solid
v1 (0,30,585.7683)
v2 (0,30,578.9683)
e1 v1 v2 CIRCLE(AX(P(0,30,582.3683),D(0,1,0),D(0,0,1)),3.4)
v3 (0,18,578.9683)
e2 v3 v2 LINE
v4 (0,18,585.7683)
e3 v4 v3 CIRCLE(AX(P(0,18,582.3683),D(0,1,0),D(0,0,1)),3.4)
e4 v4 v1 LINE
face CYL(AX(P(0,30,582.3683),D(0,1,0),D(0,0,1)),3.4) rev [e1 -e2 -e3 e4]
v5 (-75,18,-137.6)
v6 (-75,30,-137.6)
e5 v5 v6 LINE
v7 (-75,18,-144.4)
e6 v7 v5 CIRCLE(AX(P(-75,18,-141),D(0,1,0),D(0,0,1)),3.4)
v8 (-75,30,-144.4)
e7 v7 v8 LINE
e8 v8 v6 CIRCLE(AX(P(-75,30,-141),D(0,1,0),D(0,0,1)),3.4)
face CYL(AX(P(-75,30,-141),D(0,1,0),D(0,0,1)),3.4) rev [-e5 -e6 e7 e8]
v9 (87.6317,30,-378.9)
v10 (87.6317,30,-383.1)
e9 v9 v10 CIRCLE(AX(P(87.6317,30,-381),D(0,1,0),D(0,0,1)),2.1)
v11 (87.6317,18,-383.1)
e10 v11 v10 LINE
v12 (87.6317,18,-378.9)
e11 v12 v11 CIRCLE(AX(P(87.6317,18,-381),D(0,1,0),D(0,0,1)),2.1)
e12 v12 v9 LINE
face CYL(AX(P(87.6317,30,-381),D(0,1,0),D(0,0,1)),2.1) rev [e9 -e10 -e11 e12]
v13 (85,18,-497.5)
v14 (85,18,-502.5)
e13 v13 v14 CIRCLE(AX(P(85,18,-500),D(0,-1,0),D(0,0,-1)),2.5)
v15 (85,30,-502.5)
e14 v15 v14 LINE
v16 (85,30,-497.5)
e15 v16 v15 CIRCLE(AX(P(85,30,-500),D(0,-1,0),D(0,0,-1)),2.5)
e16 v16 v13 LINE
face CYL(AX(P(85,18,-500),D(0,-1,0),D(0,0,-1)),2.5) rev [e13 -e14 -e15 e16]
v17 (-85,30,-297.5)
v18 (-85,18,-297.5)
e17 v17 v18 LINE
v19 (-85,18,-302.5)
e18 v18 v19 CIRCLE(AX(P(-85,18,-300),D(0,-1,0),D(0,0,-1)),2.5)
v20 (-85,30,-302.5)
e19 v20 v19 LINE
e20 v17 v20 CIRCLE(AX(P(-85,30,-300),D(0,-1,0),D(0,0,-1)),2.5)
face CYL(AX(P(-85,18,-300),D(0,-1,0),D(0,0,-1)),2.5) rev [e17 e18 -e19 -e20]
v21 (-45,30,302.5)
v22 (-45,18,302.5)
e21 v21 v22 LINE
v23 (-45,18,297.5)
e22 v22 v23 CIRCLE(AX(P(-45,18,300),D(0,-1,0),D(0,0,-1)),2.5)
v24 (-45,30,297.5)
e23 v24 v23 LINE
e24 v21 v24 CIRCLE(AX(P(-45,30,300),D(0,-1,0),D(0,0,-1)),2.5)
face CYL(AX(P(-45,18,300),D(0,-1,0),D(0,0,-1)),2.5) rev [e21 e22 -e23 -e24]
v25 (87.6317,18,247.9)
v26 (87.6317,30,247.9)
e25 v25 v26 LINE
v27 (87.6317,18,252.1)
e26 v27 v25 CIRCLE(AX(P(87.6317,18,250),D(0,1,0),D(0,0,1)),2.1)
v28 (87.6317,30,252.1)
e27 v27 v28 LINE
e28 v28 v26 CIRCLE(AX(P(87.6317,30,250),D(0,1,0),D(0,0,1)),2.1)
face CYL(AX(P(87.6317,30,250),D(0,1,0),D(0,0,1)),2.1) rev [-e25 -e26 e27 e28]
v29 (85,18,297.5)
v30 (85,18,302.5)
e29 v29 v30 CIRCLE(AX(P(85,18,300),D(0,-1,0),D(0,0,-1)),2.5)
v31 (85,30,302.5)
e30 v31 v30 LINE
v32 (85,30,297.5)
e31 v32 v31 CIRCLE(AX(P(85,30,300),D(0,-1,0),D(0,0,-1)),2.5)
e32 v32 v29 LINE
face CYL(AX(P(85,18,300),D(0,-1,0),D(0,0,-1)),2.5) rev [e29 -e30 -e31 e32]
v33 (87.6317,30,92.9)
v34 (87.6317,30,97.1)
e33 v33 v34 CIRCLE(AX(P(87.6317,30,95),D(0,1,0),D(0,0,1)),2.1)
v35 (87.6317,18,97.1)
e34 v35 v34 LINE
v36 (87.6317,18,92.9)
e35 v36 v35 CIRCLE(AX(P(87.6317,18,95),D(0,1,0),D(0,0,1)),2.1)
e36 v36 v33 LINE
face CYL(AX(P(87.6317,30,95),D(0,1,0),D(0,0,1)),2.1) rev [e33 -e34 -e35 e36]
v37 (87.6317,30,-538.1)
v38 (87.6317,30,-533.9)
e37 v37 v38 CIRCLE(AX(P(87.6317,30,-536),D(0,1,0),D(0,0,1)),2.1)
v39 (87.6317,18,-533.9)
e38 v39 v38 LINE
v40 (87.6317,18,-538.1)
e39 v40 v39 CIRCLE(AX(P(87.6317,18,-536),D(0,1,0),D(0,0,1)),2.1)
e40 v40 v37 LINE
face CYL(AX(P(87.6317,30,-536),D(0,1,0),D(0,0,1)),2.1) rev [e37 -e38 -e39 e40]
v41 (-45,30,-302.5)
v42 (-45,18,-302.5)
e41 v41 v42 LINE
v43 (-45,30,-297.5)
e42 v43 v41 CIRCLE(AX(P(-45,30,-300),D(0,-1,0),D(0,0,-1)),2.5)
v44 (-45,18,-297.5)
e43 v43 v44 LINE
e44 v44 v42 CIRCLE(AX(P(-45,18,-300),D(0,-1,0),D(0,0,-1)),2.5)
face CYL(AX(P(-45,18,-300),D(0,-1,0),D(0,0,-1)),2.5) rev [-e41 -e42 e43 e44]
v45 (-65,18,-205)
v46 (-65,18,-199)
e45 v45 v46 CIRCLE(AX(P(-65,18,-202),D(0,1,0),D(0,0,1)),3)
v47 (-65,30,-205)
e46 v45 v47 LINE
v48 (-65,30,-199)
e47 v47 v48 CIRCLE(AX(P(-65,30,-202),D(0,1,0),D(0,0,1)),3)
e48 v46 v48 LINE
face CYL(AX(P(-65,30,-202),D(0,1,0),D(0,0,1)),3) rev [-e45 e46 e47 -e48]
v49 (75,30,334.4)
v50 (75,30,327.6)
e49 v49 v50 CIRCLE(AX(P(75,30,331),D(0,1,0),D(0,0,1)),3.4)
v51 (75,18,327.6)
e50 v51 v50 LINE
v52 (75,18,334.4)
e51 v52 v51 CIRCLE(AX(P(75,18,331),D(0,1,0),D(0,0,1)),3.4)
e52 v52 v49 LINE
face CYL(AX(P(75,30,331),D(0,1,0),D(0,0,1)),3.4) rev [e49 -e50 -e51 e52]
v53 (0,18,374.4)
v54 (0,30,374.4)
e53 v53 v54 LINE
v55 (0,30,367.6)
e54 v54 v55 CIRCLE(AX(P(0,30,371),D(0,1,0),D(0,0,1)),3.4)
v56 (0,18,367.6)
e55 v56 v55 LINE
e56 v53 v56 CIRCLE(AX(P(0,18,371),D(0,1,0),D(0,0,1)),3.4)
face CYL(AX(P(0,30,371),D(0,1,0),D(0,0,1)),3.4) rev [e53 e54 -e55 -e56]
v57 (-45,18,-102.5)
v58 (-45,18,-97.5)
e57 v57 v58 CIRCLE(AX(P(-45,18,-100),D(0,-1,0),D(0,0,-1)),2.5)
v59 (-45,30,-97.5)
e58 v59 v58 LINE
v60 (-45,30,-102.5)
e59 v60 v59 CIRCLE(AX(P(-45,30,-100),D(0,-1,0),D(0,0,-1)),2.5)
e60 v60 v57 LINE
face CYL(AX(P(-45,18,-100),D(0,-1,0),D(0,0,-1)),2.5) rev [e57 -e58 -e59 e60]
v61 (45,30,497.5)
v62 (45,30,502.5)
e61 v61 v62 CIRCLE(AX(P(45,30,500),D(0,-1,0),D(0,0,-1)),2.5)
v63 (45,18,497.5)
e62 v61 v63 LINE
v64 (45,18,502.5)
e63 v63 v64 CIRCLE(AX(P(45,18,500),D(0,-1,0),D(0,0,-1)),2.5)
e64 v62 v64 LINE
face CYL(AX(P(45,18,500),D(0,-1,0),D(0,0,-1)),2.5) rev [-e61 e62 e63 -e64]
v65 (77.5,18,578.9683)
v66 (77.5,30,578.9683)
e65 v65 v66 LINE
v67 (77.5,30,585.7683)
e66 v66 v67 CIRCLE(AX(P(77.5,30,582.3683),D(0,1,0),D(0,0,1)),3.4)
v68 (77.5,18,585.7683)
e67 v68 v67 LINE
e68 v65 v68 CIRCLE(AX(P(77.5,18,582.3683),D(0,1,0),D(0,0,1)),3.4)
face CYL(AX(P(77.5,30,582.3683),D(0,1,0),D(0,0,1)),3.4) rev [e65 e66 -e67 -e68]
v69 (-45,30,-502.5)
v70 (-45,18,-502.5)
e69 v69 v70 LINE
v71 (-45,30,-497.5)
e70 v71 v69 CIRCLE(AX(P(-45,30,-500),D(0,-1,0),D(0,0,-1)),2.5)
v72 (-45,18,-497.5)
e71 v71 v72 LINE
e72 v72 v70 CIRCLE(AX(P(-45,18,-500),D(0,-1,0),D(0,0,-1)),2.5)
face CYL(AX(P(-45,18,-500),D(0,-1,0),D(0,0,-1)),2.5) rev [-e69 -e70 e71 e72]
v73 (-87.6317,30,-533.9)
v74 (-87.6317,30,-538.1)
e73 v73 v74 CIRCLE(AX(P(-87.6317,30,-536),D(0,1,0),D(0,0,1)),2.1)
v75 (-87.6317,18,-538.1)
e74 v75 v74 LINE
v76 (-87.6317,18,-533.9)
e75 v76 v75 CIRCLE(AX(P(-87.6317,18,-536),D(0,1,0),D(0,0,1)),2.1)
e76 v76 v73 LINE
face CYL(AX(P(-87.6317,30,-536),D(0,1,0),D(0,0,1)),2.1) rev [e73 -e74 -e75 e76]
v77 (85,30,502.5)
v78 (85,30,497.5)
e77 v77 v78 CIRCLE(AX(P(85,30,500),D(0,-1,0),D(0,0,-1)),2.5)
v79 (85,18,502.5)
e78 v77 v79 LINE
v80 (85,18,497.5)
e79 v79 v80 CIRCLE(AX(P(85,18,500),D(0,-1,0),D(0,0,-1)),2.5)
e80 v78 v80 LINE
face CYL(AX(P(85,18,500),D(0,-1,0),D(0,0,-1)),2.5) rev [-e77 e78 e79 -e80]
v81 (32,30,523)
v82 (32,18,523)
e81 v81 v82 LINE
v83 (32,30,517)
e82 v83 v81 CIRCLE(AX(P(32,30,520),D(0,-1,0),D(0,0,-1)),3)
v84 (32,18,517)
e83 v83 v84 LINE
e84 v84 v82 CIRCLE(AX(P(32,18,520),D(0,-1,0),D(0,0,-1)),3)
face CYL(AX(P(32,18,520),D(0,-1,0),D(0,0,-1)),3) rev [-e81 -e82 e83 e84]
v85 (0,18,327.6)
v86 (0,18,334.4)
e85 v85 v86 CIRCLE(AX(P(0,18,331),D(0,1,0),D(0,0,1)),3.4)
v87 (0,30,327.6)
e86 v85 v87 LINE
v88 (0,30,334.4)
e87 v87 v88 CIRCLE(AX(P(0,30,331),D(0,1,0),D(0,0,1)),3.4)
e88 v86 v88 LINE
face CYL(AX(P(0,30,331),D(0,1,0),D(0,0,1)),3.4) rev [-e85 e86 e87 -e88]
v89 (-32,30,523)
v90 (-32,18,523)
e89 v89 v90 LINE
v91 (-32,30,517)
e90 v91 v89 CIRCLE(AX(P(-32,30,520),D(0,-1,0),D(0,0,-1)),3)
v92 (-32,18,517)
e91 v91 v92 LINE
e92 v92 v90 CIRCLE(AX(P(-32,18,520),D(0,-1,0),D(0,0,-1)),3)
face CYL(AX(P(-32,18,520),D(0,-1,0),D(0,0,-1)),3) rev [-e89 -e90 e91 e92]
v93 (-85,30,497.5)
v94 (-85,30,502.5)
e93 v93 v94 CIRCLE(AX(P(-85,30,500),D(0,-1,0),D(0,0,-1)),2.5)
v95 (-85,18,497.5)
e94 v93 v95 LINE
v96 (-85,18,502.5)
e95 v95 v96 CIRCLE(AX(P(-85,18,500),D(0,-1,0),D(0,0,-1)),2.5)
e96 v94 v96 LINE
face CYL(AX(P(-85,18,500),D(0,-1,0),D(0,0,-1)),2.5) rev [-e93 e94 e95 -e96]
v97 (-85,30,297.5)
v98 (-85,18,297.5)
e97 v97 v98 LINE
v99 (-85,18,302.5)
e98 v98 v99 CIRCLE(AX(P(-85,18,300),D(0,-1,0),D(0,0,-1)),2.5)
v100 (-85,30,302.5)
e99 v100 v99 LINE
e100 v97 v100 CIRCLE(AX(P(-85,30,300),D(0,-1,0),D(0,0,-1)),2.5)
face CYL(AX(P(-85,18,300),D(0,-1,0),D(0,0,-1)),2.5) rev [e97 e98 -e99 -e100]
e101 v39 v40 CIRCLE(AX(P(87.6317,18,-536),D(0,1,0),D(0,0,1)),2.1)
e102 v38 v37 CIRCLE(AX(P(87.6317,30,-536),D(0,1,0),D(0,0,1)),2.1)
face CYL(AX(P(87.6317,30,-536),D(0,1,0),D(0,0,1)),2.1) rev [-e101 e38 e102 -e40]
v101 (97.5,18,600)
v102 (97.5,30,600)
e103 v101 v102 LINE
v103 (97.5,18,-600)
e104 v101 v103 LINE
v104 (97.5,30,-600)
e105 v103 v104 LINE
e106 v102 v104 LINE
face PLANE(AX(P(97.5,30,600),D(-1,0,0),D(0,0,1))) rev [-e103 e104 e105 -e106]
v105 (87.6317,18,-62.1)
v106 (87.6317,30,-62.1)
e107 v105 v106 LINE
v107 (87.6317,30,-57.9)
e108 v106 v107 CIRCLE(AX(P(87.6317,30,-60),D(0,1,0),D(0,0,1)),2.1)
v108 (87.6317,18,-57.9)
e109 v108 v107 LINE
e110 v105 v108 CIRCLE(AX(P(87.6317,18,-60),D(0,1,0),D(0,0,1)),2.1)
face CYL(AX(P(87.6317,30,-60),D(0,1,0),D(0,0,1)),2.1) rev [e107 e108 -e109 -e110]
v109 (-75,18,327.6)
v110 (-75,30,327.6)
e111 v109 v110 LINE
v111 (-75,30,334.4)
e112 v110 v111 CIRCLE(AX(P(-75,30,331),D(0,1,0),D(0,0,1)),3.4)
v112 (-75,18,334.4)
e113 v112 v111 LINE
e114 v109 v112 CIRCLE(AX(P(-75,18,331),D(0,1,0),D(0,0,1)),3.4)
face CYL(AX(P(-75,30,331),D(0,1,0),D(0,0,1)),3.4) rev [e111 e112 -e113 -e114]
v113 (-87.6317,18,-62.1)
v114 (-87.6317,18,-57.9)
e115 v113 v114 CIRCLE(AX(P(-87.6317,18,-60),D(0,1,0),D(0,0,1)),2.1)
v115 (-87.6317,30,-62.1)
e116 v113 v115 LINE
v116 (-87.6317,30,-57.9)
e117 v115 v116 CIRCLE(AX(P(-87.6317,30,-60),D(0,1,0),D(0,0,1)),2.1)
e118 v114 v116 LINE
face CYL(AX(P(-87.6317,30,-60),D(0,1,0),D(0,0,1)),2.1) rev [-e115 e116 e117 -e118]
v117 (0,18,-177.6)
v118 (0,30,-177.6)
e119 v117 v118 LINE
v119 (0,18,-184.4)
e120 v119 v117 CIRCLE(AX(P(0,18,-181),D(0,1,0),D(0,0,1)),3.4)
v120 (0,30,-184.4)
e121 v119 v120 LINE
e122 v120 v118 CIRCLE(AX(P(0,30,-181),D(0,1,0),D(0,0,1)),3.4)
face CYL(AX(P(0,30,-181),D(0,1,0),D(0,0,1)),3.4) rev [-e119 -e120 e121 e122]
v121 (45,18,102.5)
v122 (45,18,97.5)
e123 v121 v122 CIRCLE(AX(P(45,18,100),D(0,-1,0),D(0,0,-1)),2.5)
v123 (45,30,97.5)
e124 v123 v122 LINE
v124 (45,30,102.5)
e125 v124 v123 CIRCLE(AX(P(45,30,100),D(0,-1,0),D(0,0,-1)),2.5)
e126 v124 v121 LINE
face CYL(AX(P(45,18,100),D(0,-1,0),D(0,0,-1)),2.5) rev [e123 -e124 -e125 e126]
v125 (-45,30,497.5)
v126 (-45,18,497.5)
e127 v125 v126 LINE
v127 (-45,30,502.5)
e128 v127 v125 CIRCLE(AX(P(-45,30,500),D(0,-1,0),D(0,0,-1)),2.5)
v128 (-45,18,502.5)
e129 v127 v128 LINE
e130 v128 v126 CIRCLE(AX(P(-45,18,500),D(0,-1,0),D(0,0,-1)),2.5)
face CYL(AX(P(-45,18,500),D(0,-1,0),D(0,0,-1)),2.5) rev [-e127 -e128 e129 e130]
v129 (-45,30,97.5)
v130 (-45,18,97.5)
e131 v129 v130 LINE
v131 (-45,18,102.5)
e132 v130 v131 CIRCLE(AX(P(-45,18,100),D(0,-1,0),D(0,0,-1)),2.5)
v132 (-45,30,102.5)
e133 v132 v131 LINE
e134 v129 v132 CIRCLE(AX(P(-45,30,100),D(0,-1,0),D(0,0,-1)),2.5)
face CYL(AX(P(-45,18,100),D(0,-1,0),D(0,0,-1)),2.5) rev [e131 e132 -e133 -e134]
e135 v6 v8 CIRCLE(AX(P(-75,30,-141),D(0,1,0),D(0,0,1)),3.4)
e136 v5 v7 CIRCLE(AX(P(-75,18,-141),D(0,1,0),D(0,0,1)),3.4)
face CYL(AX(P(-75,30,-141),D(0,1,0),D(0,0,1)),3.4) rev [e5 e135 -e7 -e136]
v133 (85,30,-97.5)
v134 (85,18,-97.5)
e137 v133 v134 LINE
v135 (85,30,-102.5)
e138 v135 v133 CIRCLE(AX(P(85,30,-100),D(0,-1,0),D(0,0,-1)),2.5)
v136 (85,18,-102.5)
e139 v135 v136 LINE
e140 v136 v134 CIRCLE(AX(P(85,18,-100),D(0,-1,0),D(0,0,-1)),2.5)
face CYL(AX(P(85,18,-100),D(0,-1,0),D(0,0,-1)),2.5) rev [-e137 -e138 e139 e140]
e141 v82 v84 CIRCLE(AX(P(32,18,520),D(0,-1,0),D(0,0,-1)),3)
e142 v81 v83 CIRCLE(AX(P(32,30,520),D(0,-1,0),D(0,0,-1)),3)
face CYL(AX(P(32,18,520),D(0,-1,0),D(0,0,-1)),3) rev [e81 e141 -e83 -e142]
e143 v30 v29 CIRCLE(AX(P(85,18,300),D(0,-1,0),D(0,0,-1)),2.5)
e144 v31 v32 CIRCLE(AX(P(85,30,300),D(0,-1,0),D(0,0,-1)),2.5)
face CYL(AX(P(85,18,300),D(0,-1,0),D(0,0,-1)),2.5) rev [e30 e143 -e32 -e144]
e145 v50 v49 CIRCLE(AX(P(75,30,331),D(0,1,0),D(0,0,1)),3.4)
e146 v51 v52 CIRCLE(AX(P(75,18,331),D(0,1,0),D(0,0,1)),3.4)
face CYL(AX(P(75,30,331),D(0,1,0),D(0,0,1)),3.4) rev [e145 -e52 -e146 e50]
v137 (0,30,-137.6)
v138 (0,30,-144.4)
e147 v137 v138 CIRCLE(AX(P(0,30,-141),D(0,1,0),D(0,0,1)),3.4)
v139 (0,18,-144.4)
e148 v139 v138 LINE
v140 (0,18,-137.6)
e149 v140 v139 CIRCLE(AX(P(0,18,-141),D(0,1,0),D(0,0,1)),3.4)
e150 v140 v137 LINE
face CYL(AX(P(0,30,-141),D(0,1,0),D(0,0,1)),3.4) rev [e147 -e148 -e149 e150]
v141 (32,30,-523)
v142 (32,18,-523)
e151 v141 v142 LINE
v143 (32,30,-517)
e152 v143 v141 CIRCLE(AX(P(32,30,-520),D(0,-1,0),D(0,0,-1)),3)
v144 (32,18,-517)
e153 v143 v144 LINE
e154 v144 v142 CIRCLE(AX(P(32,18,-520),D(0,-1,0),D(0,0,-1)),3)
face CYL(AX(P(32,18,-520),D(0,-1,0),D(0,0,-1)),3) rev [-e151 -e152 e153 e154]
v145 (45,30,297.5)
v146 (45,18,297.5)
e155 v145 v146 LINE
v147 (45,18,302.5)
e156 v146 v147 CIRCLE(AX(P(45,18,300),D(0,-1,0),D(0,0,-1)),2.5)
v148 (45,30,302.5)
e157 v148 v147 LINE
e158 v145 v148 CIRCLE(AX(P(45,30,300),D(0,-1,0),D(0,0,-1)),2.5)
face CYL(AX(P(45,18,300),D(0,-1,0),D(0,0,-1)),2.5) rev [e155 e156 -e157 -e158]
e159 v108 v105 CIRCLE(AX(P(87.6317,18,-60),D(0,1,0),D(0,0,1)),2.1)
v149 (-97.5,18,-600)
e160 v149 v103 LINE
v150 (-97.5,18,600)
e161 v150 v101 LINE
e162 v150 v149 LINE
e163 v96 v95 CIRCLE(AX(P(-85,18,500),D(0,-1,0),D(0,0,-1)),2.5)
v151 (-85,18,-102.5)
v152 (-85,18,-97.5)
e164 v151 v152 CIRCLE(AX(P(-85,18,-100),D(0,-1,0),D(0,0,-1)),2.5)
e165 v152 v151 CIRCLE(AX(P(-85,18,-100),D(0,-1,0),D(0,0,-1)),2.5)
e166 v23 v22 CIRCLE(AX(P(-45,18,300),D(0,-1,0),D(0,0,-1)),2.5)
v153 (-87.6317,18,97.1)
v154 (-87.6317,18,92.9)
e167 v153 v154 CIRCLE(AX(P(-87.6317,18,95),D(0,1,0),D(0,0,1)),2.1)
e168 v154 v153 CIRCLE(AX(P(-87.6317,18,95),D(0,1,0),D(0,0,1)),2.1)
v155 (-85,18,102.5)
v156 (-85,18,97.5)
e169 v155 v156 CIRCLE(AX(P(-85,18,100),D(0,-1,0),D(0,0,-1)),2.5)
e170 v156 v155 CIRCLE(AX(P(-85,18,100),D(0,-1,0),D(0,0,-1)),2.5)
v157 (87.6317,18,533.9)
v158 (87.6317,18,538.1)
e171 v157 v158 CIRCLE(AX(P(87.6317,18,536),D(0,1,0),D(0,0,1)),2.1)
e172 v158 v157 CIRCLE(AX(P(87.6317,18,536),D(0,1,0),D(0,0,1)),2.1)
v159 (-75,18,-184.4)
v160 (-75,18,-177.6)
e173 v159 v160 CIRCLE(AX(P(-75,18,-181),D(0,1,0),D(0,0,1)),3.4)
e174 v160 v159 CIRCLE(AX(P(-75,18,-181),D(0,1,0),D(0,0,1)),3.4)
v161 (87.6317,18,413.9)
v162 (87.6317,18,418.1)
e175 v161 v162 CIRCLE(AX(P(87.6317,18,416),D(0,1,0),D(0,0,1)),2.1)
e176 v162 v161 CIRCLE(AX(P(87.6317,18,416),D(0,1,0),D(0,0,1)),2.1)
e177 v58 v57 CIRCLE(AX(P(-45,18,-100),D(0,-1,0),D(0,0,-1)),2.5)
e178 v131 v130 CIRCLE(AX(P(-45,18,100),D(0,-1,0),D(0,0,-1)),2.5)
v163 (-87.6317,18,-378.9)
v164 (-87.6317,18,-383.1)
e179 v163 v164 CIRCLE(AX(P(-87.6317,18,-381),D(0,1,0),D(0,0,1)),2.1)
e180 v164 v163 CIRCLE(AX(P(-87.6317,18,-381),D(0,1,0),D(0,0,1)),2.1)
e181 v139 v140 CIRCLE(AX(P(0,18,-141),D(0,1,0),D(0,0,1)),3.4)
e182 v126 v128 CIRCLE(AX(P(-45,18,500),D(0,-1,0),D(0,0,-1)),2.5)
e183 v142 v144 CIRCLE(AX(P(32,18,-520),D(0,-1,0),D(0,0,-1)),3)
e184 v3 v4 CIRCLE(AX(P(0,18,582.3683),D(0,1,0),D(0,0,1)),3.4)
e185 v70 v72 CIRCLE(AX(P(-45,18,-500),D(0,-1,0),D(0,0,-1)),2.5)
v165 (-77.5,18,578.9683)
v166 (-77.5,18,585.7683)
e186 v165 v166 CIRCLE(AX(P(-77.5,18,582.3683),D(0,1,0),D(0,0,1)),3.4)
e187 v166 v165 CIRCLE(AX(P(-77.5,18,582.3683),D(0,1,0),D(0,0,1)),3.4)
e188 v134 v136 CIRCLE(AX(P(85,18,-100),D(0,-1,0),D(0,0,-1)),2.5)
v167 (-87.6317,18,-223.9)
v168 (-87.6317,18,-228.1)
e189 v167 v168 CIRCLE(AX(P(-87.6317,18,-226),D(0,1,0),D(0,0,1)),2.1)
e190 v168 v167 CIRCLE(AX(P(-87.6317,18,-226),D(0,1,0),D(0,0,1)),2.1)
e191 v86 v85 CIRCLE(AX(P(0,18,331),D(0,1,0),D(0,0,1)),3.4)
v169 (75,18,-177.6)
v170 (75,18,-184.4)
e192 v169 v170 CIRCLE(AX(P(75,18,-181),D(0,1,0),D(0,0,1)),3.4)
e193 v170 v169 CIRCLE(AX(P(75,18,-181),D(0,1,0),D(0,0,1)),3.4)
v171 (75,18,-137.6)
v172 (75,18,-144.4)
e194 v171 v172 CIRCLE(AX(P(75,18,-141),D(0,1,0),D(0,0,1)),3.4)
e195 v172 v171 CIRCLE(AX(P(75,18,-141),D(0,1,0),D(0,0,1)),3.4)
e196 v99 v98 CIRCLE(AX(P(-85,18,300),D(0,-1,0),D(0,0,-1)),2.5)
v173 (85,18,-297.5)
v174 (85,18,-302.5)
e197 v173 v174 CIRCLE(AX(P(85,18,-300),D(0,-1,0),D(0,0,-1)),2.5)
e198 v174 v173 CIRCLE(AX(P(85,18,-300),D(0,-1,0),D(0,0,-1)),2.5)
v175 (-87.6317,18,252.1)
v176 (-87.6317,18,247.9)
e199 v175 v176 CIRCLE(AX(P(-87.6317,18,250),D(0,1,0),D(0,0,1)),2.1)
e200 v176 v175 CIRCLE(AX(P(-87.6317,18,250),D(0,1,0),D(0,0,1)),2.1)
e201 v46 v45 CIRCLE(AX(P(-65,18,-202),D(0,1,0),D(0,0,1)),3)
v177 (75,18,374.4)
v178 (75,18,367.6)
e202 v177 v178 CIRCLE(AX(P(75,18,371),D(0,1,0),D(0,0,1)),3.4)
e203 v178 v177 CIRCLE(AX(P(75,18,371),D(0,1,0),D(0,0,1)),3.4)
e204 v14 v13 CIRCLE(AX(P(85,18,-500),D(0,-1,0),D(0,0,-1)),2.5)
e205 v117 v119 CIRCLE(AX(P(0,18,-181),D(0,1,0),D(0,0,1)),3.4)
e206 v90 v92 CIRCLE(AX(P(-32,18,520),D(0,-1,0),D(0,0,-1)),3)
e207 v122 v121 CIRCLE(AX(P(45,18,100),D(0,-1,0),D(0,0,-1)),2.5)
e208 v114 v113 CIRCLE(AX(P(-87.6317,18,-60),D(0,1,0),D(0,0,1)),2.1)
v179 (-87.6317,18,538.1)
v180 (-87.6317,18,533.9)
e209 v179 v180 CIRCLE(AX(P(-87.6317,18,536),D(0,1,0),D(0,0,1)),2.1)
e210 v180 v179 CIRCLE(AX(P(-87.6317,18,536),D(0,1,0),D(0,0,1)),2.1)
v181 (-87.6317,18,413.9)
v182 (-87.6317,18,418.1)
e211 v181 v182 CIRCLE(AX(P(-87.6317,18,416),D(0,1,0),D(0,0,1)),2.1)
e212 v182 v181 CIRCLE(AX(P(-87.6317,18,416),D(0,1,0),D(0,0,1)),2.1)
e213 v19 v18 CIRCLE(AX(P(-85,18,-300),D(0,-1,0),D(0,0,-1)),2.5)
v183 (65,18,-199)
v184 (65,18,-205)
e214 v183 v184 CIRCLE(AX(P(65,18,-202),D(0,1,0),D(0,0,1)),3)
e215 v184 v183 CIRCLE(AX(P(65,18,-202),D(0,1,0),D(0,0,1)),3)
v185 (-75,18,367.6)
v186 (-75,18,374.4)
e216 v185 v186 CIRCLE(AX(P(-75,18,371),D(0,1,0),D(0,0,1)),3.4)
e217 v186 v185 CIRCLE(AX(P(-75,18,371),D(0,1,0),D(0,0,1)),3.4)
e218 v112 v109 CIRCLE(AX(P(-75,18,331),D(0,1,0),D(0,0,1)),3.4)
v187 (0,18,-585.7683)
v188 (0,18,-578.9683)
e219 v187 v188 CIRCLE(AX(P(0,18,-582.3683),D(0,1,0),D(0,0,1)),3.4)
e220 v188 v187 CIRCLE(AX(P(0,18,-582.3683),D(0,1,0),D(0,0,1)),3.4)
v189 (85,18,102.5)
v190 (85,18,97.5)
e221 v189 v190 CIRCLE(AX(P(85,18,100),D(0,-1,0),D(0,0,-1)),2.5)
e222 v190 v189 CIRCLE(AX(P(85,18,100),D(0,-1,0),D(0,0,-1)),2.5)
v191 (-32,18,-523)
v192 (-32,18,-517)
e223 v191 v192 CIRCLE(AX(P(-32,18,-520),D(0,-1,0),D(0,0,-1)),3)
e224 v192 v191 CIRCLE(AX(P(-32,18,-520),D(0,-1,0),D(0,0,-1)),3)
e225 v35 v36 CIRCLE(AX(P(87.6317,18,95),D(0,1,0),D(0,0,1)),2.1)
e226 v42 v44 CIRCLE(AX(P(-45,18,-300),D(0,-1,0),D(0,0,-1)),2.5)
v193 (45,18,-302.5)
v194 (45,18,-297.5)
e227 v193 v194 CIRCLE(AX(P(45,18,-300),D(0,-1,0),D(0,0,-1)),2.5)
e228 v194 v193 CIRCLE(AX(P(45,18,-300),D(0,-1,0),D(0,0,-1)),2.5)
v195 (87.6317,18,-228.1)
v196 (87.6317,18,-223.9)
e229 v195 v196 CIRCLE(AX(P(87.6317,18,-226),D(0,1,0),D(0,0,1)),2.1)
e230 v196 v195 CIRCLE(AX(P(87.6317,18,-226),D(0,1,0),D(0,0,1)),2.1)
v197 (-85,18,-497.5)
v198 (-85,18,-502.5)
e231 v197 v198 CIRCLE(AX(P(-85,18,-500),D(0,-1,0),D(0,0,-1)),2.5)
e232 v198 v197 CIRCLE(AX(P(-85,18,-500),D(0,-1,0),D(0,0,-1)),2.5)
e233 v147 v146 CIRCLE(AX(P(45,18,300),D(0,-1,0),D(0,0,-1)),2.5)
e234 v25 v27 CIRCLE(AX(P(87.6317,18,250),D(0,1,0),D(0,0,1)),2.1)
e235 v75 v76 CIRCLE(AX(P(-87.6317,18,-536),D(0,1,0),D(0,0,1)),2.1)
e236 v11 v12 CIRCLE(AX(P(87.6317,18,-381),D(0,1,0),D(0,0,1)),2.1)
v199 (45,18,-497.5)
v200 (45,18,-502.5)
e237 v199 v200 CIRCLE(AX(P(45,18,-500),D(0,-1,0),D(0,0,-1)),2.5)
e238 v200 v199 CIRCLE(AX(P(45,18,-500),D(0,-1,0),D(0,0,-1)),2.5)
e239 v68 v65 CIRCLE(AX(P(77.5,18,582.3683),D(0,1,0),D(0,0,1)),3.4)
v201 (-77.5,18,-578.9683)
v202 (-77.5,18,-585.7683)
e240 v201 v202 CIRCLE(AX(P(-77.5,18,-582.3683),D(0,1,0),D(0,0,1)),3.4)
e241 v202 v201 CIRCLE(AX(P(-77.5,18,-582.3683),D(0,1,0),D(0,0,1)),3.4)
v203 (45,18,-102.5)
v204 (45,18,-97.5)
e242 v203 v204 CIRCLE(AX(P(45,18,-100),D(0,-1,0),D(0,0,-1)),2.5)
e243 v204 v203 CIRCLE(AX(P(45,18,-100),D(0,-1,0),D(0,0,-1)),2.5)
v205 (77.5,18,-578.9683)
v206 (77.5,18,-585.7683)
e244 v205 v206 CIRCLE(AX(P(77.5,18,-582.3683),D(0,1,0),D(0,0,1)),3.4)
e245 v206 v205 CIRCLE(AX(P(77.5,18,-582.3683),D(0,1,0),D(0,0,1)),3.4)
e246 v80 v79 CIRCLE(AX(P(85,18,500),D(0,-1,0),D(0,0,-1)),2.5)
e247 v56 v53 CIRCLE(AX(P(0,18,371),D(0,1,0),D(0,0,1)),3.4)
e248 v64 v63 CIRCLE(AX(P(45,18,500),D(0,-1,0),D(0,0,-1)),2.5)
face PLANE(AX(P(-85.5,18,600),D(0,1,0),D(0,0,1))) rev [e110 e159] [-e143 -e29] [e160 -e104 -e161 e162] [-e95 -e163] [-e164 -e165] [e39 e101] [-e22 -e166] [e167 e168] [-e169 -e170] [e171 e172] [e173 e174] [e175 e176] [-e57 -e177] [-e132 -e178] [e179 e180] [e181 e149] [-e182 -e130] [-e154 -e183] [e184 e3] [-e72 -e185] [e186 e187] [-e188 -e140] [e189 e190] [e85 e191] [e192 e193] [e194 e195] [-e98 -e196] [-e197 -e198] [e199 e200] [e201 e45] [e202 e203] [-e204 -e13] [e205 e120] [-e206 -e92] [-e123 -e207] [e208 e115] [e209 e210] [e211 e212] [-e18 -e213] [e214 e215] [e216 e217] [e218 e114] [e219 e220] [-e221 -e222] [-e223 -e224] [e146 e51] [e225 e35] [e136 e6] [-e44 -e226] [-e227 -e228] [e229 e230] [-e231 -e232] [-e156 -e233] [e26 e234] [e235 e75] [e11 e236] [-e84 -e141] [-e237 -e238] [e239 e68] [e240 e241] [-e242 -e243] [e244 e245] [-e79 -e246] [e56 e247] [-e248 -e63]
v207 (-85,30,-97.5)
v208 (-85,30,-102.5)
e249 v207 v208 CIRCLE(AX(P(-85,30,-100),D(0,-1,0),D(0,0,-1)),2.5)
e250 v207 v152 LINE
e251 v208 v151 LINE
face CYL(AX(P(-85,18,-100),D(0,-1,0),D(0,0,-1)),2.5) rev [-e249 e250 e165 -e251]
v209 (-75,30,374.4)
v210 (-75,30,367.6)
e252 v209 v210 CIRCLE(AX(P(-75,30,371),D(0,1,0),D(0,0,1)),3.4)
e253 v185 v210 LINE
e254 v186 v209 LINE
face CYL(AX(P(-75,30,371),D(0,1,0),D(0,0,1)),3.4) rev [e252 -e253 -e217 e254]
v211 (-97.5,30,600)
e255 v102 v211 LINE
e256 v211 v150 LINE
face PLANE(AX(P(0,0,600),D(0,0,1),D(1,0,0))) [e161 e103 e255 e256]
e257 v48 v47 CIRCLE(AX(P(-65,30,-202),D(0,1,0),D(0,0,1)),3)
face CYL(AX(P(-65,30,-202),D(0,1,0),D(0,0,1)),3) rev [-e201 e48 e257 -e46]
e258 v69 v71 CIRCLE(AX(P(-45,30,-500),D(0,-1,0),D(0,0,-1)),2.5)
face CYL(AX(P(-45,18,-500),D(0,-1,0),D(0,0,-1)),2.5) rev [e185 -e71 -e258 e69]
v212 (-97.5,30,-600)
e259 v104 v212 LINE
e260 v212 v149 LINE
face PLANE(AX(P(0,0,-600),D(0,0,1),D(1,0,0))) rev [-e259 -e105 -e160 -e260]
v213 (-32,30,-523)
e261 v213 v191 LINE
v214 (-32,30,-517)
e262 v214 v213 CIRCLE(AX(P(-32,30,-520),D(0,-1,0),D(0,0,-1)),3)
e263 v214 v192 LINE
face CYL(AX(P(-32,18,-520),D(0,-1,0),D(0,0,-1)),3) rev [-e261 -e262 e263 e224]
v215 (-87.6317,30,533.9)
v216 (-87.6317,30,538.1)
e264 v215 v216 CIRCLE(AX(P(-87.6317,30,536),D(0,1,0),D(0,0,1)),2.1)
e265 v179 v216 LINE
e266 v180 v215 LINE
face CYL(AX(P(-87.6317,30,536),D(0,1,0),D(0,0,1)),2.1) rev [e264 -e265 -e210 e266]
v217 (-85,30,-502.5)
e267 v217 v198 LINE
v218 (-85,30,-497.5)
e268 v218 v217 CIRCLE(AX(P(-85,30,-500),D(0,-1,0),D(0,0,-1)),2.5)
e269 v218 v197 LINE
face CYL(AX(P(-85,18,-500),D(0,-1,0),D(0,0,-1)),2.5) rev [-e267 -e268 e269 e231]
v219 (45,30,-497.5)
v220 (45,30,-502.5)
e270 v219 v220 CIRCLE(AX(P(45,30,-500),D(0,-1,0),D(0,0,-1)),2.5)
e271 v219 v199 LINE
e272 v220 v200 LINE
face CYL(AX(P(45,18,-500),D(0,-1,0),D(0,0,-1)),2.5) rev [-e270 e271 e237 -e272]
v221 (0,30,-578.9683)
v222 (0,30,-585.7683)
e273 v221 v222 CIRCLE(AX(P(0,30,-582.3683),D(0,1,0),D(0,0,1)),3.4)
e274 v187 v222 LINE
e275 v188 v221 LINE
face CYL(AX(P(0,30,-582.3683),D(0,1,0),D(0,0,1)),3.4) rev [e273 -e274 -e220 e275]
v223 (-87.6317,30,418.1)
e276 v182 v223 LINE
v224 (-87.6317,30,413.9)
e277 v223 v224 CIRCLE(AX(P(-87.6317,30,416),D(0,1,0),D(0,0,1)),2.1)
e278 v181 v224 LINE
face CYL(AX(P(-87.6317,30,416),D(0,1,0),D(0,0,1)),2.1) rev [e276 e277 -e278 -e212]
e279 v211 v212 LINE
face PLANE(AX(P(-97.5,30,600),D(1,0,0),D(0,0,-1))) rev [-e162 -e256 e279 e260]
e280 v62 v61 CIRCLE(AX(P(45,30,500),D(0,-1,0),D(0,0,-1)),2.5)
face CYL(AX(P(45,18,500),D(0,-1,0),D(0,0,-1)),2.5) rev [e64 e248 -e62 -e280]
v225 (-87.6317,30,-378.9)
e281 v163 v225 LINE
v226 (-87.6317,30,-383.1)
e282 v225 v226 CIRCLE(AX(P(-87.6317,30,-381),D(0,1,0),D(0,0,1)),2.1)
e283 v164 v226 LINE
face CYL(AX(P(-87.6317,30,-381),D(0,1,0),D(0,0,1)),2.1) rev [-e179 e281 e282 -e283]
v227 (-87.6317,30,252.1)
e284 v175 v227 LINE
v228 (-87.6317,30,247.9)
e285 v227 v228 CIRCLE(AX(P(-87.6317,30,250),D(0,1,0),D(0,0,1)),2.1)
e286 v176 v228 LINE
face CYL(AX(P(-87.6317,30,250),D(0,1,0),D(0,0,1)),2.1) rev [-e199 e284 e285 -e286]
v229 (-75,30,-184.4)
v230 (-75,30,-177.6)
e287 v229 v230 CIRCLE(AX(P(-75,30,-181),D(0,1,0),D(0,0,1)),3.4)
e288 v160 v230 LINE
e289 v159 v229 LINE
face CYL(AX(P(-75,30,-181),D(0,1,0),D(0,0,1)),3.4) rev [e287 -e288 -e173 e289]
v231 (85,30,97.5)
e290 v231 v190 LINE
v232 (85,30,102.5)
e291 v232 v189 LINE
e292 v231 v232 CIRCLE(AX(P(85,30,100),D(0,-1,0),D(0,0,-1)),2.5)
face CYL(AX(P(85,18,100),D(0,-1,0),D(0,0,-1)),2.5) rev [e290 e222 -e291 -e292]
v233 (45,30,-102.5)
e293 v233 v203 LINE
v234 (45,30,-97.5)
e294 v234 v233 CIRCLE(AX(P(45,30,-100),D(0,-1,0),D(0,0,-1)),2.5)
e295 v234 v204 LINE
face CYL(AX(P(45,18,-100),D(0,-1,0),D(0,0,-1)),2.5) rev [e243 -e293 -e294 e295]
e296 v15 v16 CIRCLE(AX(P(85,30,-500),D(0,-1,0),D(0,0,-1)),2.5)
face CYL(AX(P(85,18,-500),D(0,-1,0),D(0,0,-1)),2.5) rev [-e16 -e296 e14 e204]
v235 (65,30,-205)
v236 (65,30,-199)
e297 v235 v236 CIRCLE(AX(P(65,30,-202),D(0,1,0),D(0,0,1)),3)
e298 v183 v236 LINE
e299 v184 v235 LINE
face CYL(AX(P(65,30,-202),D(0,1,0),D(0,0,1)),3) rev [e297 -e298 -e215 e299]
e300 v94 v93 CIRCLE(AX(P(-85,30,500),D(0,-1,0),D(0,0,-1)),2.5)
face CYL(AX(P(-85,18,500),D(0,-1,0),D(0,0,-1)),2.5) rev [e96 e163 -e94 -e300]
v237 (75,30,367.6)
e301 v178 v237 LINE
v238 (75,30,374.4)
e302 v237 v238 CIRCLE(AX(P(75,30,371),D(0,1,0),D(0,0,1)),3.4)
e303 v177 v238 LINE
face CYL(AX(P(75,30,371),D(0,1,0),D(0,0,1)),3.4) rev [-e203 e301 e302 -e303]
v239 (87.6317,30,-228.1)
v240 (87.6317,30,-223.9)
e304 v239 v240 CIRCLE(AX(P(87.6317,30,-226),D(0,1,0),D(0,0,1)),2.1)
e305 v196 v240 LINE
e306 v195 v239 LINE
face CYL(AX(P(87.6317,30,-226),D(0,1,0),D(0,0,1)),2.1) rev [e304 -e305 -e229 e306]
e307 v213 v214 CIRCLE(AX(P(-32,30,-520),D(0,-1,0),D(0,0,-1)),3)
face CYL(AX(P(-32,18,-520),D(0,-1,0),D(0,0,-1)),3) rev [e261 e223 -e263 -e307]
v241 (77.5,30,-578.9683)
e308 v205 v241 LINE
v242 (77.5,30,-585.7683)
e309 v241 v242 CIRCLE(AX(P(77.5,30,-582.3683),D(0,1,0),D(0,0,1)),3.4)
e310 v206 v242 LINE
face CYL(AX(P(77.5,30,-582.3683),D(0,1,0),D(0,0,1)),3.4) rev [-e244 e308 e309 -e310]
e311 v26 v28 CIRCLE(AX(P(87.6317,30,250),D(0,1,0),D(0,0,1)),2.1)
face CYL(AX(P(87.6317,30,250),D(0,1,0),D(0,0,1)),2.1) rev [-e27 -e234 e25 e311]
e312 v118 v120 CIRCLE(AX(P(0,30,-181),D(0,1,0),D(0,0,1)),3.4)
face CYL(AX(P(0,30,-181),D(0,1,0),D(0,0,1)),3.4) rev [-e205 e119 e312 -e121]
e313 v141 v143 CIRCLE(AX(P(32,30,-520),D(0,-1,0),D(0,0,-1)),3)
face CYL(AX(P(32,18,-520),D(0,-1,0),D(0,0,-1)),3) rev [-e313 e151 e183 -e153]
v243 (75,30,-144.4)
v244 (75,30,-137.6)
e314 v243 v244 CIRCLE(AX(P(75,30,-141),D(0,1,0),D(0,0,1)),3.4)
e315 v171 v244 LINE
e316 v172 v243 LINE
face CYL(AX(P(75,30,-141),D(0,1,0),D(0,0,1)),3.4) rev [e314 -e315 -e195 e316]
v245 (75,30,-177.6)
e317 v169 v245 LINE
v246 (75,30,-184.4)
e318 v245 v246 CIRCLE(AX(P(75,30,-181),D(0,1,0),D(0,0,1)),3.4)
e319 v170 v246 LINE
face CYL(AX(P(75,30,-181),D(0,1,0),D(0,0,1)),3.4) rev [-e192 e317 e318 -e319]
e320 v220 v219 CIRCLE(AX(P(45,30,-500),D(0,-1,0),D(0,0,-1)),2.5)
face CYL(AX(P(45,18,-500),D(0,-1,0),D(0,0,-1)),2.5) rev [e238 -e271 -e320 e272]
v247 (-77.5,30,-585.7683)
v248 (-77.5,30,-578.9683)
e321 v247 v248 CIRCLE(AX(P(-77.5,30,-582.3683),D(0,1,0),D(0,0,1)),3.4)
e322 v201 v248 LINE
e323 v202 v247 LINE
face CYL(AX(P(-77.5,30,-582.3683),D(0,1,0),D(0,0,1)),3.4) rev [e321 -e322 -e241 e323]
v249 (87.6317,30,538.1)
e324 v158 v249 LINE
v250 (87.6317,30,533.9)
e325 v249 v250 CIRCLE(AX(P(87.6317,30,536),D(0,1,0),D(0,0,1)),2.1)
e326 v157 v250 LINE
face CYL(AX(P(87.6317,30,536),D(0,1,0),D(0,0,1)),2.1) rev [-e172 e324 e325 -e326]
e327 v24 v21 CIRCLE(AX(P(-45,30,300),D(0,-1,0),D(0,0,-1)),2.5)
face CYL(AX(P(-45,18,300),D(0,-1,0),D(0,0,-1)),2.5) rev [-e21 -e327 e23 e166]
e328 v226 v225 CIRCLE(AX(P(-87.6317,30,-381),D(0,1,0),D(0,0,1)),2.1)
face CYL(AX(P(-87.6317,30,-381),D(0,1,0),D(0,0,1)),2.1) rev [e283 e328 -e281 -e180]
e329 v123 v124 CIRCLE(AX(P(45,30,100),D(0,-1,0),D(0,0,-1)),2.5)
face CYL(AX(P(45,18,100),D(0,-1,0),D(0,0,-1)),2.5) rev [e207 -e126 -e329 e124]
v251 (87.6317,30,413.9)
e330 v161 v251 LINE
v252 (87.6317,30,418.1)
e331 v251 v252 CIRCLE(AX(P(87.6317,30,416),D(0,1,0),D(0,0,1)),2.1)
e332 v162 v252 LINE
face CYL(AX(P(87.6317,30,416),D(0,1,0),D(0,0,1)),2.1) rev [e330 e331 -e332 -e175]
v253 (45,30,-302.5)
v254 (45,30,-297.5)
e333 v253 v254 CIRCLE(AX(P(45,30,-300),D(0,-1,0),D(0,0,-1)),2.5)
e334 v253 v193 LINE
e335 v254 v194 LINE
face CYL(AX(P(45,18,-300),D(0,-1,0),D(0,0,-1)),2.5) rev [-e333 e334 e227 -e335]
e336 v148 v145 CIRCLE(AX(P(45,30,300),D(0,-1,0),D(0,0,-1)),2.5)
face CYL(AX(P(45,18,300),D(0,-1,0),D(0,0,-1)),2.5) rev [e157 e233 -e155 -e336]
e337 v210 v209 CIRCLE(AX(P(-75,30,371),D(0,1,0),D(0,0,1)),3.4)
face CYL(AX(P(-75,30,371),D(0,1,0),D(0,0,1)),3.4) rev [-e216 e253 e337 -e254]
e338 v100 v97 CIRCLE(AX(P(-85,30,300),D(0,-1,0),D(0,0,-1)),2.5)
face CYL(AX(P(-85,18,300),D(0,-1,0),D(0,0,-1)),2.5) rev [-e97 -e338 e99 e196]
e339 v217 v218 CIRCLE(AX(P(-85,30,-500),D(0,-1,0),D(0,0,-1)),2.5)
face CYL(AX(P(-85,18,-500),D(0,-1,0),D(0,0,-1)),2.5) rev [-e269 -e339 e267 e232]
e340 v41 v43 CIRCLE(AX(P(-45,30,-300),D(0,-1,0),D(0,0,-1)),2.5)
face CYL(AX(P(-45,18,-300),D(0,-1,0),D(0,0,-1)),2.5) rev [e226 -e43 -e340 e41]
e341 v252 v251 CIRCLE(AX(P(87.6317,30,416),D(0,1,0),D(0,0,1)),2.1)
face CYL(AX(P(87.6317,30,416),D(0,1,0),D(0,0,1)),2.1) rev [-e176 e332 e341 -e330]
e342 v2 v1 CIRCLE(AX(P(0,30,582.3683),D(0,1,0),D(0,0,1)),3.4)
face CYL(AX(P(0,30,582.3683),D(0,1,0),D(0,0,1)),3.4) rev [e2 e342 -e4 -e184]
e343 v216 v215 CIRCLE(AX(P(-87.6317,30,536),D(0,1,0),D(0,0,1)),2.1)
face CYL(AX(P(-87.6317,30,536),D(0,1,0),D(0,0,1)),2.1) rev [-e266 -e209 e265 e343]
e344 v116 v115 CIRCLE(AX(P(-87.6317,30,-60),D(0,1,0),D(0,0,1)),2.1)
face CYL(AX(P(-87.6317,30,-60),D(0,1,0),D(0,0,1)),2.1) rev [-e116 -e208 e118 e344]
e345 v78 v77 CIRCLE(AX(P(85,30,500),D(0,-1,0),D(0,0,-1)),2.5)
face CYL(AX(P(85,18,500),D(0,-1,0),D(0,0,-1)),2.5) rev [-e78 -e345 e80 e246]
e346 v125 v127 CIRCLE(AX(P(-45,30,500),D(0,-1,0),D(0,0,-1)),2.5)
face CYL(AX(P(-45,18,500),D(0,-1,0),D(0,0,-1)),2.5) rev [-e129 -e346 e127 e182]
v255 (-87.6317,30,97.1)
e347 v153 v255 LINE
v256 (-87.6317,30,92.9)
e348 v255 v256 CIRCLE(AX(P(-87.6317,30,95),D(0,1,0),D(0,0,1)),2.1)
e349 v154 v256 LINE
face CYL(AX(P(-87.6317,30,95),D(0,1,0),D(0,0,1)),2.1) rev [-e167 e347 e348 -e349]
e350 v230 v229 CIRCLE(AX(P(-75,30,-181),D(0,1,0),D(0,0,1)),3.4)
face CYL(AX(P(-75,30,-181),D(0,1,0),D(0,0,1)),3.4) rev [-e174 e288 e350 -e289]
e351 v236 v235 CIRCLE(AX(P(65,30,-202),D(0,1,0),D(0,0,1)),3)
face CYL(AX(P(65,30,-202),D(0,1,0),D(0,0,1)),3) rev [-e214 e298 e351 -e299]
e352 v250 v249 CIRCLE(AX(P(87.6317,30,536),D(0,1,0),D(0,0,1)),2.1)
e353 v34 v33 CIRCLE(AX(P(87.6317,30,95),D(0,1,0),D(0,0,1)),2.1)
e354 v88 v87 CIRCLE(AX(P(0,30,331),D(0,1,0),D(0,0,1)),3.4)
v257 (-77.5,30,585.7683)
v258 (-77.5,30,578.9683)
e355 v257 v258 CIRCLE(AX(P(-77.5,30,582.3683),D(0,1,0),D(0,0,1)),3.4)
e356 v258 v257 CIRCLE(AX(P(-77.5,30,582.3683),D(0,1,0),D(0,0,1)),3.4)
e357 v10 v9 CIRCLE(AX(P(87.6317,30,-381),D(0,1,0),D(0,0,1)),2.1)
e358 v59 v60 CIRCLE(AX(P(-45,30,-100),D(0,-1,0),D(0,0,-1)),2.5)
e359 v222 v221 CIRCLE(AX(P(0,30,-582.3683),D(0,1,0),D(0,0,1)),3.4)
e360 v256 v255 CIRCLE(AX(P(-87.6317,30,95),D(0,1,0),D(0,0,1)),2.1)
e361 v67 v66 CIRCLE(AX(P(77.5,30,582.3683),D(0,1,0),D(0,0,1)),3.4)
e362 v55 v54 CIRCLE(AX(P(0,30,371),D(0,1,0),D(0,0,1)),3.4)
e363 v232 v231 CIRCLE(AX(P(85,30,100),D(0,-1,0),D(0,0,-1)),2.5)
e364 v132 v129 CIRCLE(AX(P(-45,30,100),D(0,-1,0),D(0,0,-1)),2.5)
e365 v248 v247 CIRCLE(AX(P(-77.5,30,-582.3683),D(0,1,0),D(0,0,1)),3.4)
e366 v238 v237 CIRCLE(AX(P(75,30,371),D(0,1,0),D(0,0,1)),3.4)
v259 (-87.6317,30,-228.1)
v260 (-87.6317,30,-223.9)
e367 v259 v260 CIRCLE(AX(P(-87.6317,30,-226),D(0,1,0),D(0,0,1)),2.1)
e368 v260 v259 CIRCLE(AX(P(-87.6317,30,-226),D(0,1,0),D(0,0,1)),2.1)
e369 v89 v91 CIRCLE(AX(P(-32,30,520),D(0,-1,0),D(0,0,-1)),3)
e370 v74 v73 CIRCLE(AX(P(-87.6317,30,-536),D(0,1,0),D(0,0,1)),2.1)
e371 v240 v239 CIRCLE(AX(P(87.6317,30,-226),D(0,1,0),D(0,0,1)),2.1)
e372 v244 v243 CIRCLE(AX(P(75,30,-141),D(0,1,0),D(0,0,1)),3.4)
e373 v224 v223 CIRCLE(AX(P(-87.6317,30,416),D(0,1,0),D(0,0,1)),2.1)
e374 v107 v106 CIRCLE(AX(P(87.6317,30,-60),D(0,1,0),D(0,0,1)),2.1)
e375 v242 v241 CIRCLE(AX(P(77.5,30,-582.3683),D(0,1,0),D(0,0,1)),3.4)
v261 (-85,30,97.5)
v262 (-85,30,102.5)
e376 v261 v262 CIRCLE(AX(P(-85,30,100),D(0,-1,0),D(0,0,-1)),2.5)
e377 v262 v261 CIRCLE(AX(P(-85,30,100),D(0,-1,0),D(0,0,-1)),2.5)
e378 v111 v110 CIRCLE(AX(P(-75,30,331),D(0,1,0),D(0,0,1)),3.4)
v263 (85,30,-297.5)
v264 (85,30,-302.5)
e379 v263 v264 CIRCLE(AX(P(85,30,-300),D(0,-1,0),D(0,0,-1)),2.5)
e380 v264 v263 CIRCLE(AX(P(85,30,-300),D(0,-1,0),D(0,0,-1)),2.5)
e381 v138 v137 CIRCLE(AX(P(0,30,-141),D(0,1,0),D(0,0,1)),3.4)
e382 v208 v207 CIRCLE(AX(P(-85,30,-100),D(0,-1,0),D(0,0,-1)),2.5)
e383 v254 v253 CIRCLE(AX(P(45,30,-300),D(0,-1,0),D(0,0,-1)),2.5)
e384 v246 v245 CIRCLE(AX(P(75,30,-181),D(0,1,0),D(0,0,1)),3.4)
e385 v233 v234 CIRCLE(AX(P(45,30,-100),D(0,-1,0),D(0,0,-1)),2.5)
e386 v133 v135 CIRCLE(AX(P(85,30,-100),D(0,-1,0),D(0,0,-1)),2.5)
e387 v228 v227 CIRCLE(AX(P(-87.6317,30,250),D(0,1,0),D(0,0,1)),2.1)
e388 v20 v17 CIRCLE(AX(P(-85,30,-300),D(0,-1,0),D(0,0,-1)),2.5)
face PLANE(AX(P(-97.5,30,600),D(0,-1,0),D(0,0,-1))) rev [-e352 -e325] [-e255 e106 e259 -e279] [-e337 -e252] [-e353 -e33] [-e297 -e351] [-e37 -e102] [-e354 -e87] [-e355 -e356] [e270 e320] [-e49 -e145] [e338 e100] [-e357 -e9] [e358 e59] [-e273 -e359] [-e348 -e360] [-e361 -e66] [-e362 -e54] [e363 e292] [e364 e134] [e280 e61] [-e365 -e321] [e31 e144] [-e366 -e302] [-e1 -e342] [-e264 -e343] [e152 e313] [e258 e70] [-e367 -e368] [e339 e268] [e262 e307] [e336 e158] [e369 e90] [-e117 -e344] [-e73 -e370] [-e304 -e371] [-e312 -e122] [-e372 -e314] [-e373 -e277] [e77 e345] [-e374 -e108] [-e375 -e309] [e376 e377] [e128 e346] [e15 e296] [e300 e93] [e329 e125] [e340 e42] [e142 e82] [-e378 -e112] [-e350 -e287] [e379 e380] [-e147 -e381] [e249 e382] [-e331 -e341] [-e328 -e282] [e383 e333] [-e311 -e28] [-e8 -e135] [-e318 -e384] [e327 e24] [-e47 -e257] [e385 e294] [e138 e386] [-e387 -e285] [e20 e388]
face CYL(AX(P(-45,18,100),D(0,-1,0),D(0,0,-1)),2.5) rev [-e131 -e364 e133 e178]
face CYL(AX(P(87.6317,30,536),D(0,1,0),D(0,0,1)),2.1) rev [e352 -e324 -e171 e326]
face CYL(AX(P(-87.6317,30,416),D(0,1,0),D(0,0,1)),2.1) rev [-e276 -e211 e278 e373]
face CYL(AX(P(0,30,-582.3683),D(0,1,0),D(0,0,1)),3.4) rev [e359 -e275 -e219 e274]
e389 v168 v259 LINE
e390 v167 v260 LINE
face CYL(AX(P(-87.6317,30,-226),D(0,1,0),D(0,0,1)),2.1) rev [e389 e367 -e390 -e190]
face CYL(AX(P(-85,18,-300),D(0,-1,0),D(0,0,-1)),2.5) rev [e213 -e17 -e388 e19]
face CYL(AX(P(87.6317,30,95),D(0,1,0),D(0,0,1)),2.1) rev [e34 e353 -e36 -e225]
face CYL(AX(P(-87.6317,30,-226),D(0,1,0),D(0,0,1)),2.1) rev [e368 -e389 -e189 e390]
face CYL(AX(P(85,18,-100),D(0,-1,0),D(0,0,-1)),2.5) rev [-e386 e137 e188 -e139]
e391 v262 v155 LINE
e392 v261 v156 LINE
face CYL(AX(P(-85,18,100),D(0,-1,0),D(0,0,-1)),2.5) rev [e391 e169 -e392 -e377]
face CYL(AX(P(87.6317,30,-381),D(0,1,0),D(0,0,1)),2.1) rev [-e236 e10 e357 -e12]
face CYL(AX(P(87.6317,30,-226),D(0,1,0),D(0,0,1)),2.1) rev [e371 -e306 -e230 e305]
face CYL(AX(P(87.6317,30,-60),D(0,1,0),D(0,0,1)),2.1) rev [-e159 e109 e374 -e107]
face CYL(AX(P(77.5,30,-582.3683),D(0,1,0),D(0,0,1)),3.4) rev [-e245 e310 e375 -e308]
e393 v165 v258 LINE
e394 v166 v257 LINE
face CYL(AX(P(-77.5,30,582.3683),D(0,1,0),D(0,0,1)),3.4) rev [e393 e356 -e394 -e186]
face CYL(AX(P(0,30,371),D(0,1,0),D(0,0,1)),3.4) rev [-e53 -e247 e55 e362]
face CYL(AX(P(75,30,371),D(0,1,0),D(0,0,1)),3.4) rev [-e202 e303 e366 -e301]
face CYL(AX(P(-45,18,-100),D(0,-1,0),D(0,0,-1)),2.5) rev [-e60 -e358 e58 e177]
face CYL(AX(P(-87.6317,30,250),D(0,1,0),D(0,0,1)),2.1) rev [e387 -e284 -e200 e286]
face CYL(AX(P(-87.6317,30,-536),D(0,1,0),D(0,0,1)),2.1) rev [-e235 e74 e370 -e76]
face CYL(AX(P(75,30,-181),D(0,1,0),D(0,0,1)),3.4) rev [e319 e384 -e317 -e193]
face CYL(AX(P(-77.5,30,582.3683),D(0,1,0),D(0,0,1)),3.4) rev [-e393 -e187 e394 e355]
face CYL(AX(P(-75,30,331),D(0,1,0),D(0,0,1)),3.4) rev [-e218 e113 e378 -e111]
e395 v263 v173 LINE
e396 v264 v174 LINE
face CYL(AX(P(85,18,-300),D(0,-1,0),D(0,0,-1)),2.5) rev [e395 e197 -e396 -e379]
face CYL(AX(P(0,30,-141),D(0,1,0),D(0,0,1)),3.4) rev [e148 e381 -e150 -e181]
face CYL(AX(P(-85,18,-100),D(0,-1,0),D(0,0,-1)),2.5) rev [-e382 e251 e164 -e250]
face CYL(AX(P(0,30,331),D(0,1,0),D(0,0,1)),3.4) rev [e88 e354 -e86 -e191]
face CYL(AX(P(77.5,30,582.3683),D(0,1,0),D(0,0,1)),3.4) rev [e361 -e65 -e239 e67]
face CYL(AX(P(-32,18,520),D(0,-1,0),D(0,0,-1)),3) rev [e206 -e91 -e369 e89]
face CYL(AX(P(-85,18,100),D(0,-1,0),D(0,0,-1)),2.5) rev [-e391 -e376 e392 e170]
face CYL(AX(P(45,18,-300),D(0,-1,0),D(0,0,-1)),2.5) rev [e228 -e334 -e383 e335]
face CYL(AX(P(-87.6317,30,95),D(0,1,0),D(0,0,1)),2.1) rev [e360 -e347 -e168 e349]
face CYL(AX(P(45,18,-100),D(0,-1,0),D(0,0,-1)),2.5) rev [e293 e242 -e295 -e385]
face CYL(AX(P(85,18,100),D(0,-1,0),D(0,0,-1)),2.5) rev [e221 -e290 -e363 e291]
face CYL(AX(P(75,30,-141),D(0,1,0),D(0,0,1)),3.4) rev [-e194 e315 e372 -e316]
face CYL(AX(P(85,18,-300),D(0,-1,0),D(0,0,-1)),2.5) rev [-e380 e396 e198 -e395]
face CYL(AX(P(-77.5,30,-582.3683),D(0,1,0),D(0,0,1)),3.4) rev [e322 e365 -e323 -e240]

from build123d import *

# Parameters (mm, degrees)
EXTRUDE_1_DEPTH     = 600
SKETCH_2_W          = 195
SKETCH_2_H          = 38
CUT_EXTRUDE_1_DEPTH = 1205.328132197
HOLE_WIZARD_M6_1_D  = 5
HOLE_WIZARD_M8_1_D  = 6.8
F_6_0MM_1_D         = 6
HOLE_WIZARD_M5_1_D  = 4.2
HOLE_WIZARD_M8_2_D  = 6.8
F_6_0MM_2_D         = 6


with BuildPart() as part:
    # 草图1 → 凸台-拉伸1 (new, symmetric)
    with BuildSketch(Plane.XY):
        Polygon((-97.5, 30), (97.5, 30), (97.5, -20), (85.5, -20), (85.5, 18), (-85.5, 18), (-85.5, -20), (-97.5, -20), align=None)
    extrude(amount=EXTRUDE_1_DEPTH, both=True)

    # 草图2 → 切除-拉伸1 (cut, through all)
    with BuildSketch(Plane(origin=(0, 0, -600), x_dir=(-1, 0, 0), z_dir=(0, 0, -1))):
        with Locations((0, -1)):
            Rectangle(SKETCH_2_W, SKETCH_2_H)
    extrude(amount=-CUT_EXTRUDE_1_DEPTH, mode=Mode.SUBTRACT)

    # M6 螺纹孔1 (through all)
    with Locations(Plane(origin=(0, 18, 0), x_dir=(-1, 0, 0), z_dir=(0, -1, 0))):
        with Locations((45, 500), (85, 500), (45, 300), (85, 300), (45, 100), (85, 100), (45, -100), (85, -100), (45, -300), (85, -300), (45, -500), (85, -500), (-85, 500), (-45, 500), (-85, 300), (-45, 300), (-85, 100), (-45, 100), (-85, -100), (-45, -100), (-85, -300), (-45, -300), (-85, -500), (-45, -500)):
            Hole(HOLE_WIZARD_M6_1_D / 2)

    # M8 螺纹孔1 (through all)
    with Locations(Plane(origin=(0, 30, 0), x_dir=(1, 0, 0), z_dir=(0, 1, 0))):
        with Locations((-77.5, 582.3683), (0, 582.3683), (77.5, 582.3683), (-77.5, -582.3683), (0, -582.3683), (77.5, -582.3683)):
            Hole(HOLE_WIZARD_M8_1_D / 2)

    # Ø6.0mm 暗销孔1 (through all)
    with Locations(Plane(origin=(0, 18, 0), x_dir=(-1, 0, 0), z_dir=(0, -1, 0))):
        with Locations((32, 520), (-32, 520), (-32, -520), (32, -520)):
            Hole(F_6_0MM_1_D / 2)

    # M5 螺纹孔1 (through all)
    with Locations(Plane(origin=(0, 30, 0), x_dir=(1, 0, 0), z_dir=(0, 1, 0))):
        with Locations((87.6317, 536), (87.6317, 381), (87.6317, 226), (87.6317, 60), (87.6317, -95), (87.6317, -250), (87.6317, -416), (87.6317, -536), (-87.6317, -536), (-87.6317, -416), (-87.6317, -250), (-87.6317, -95), (-87.6317, 60), (-87.6317, 226), (-87.6317, 381), (-87.6317, 536)):
            Hole(HOLE_WIZARD_M5_1_D / 2)

    # M8 螺纹孔2 (through all)
    with Locations(Plane(origin=(0, 30, 0), x_dir=(1, 0, 0), z_dir=(0, 1, 0))):
        with Locations((-75, -331), (-75, -371), (0, -331), (0, -371), (75, -331), (75, -371), (-75, 181), (-75, 141), (0, 181), (0, 141), (75, 181), (75, 141)):
            Hole(HOLE_WIZARD_M8_2_D / 2)

    # Ø6.0mm 暗销孔2 (through all)
    with Locations(Plane(origin=(0, 30, 0), x_dir=(1, 0, 0), z_dir=(0, 1, 0))):
        with Locations((-65, 202), (65, 202)):
            Hole(F_6_0MM_2_D / 2)


solid = part.part
